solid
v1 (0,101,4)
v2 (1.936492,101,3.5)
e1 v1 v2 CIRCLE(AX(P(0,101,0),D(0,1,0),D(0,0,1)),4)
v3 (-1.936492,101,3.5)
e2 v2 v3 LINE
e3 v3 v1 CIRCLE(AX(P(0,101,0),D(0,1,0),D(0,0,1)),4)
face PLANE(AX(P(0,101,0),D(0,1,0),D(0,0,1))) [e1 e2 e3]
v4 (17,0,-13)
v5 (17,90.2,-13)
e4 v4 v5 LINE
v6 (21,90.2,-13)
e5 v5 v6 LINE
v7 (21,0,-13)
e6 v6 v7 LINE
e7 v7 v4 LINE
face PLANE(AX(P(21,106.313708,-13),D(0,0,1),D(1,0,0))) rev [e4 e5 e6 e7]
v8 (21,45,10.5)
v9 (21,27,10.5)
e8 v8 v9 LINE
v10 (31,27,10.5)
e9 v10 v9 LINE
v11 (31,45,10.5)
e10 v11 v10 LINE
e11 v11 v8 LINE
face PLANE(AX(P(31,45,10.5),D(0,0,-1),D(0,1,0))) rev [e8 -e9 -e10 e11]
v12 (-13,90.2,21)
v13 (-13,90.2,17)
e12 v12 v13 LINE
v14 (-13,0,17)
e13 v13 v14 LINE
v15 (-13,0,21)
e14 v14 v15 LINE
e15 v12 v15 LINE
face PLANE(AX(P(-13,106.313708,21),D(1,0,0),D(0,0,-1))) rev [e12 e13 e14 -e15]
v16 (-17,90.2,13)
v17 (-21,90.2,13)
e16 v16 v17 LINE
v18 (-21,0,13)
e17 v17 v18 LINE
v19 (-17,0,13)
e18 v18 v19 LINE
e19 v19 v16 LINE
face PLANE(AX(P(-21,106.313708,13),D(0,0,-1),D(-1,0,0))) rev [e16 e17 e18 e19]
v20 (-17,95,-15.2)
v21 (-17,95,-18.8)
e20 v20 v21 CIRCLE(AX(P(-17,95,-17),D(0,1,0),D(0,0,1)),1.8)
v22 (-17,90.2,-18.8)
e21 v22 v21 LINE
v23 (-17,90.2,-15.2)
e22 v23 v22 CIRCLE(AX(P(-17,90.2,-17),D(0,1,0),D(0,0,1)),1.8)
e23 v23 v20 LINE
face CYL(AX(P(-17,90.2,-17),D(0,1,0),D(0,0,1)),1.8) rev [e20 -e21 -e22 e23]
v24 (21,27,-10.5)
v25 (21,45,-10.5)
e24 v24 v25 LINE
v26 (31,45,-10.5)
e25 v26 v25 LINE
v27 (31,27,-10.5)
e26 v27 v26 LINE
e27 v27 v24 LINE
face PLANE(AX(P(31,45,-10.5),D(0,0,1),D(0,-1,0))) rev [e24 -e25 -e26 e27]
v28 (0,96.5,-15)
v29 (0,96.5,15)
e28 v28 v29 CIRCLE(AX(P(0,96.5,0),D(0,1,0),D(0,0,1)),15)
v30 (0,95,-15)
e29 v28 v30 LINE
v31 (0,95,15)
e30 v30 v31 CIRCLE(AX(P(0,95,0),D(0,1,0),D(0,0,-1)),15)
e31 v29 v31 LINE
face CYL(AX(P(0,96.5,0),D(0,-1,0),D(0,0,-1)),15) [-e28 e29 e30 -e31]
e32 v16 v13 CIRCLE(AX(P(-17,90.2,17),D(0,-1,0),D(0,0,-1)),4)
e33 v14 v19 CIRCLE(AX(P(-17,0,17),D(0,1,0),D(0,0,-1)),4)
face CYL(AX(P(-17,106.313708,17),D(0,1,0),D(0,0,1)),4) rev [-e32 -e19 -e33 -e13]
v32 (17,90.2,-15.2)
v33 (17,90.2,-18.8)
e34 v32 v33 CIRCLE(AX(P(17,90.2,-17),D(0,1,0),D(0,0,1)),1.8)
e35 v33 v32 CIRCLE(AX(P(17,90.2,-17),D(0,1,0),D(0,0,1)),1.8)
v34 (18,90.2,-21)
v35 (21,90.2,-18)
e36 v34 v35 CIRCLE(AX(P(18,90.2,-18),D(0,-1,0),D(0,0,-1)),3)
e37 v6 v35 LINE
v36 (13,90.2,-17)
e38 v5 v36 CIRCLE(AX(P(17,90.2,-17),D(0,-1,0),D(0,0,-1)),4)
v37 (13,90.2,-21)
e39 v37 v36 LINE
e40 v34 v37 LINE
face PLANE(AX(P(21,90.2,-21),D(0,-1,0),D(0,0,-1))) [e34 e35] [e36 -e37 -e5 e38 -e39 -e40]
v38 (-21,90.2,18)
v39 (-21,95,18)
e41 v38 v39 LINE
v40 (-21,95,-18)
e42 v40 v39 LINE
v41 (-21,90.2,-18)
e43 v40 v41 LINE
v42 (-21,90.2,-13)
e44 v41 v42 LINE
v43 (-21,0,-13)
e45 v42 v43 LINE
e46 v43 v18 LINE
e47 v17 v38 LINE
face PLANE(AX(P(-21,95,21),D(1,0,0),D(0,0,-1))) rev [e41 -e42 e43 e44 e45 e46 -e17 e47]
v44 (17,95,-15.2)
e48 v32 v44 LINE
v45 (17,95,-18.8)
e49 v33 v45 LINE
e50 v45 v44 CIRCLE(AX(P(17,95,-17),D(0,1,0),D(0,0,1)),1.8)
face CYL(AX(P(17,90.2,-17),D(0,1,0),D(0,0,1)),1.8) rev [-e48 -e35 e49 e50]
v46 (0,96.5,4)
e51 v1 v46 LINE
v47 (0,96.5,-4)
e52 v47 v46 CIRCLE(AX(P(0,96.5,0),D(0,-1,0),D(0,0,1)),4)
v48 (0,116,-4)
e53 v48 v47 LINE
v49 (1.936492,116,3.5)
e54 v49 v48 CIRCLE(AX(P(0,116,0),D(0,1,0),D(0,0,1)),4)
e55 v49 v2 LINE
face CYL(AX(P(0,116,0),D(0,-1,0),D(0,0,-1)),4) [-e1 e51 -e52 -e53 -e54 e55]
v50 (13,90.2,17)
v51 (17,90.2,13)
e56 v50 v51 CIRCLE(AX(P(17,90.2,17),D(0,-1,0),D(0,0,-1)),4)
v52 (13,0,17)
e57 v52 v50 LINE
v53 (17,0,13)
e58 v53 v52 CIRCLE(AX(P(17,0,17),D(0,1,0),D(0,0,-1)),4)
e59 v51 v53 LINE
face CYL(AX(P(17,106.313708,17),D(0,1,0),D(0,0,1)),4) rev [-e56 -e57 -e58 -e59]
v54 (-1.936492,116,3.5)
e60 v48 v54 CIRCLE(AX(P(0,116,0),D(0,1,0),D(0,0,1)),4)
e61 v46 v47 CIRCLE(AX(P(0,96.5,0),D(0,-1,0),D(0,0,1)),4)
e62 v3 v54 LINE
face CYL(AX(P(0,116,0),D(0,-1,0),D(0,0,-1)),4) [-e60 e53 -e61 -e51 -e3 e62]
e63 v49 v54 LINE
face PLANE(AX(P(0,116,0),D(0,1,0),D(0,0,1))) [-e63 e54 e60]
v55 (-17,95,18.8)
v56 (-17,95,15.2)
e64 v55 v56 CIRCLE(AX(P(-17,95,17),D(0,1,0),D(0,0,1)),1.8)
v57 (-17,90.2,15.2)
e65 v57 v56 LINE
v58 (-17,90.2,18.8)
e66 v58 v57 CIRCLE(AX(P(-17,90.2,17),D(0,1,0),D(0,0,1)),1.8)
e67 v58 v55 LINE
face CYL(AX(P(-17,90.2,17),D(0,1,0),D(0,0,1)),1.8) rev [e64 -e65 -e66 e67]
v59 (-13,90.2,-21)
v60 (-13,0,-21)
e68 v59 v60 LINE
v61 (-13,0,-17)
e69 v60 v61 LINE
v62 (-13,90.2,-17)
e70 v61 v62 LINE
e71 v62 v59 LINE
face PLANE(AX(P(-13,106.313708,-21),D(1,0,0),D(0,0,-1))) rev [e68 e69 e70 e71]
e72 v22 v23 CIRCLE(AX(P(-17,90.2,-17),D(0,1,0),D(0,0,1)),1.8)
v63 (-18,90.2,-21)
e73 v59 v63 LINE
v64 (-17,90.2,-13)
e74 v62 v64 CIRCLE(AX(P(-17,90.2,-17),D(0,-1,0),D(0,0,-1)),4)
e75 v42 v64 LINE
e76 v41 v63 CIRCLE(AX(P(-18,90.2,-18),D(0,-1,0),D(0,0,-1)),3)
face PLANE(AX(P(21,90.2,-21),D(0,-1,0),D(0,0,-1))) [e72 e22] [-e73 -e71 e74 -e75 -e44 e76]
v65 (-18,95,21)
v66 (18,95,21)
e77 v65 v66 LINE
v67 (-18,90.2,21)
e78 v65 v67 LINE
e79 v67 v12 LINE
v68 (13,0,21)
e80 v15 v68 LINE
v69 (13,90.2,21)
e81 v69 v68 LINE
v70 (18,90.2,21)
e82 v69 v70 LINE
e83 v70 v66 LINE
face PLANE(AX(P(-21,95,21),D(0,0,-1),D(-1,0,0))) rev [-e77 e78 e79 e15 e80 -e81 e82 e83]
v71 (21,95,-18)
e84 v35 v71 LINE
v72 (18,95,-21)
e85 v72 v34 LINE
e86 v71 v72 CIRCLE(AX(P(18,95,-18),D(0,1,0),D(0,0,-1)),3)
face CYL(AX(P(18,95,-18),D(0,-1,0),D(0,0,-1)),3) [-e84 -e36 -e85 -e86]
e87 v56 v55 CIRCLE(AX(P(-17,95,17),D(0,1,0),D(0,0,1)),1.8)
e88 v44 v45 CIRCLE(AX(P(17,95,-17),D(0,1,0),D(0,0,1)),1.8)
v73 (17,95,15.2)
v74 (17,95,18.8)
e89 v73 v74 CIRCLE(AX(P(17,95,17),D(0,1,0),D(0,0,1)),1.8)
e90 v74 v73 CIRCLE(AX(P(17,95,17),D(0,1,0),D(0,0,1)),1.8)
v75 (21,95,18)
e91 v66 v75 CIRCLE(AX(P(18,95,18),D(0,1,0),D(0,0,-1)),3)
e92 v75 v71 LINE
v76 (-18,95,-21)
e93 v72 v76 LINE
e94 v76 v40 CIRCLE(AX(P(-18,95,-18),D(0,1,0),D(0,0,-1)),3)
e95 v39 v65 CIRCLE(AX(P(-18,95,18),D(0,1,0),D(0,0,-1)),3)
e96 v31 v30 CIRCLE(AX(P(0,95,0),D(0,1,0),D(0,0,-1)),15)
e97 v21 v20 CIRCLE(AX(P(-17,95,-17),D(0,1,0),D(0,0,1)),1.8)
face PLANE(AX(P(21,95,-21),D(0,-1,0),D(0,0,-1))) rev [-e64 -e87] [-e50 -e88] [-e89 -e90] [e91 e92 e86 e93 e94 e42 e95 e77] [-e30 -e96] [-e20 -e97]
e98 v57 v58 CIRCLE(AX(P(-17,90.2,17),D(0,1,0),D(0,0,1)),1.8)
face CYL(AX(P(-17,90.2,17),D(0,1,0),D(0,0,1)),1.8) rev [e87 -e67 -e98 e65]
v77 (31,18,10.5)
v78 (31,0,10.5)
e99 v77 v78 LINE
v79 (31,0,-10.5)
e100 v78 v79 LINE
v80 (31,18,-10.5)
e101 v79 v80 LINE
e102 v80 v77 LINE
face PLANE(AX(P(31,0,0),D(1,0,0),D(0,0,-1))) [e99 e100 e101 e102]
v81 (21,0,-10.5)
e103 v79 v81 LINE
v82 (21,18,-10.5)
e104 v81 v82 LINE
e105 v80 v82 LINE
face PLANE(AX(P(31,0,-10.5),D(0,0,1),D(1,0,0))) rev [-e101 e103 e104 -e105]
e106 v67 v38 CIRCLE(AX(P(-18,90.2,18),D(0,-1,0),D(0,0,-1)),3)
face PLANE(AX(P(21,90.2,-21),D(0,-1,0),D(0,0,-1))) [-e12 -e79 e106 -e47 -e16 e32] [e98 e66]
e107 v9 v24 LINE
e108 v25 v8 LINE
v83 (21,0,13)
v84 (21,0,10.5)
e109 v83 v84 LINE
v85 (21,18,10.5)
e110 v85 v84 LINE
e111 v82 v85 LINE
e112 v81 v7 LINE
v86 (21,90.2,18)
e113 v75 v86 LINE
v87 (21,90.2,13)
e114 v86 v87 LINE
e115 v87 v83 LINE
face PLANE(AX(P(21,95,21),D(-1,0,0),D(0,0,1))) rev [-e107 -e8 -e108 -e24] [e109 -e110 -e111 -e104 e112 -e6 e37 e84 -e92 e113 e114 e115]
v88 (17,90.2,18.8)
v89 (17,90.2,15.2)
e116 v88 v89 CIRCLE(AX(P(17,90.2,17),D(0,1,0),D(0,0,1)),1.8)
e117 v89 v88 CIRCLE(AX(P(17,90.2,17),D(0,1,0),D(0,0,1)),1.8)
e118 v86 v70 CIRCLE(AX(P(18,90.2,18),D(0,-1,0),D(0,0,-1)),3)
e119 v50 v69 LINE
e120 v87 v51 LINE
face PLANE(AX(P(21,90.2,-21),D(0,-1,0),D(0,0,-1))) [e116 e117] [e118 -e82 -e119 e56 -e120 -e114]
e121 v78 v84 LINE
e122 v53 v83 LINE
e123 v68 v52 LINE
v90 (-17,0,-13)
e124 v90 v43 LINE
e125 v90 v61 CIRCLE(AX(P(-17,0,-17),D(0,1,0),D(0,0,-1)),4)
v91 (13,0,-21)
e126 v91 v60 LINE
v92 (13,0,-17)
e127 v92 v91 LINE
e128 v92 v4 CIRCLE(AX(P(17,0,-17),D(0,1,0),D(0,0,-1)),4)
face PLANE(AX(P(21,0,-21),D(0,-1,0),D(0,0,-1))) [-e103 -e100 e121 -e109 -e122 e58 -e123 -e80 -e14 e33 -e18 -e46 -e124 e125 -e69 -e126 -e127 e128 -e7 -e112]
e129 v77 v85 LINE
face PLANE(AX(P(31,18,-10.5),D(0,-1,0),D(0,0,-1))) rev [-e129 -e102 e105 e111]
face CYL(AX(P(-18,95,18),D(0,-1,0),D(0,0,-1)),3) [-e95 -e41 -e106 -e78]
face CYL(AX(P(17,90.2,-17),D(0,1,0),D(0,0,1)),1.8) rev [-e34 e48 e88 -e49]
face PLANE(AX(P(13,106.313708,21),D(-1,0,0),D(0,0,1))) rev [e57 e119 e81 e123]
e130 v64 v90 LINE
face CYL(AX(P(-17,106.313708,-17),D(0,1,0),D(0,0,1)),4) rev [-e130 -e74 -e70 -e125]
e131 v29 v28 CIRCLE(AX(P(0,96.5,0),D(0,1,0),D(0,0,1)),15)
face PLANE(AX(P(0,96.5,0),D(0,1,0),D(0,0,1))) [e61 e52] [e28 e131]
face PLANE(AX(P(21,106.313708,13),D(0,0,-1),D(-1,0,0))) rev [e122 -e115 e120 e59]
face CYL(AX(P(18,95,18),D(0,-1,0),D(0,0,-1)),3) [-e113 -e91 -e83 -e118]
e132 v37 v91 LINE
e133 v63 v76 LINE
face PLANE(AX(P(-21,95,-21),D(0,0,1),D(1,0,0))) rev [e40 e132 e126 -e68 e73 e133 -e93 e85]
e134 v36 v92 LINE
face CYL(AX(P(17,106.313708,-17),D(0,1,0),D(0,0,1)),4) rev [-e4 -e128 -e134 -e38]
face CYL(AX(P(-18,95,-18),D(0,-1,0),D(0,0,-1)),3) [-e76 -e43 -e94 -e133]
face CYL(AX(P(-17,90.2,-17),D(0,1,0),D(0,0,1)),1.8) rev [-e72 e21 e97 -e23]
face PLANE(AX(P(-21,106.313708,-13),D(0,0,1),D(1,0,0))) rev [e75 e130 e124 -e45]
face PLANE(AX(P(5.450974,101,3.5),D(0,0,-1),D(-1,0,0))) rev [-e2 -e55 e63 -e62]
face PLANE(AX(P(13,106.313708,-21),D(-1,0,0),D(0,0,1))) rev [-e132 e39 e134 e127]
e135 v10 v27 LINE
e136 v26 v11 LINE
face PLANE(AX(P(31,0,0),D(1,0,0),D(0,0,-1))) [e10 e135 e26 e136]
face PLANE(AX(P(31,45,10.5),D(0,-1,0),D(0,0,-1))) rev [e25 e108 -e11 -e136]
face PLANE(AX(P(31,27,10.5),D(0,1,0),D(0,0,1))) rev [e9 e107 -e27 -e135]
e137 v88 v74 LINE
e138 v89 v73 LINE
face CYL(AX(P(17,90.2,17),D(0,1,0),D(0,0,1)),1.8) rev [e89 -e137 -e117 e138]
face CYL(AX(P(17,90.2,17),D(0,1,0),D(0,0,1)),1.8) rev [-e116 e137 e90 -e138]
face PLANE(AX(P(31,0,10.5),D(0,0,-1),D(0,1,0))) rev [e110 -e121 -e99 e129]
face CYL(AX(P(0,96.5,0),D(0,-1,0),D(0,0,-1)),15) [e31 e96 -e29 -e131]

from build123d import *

# Parameters (mm, degrees)
SKETCH1_W           = 42
SKETCH1_H           = 42
BOSS_EXTRUDE1_DEPTH = 95
SKETCH2_W           = 8
SKETCH2_H           = 8
CUT_EXTRUDE1_DEPTH  = 90.2
SKETCH3_R           = 1.8
CUT_EXTRUDE2_DEPTH  = 4.8
FILLET1_R           = 4
SKETCH4_R           = 15
BOSS_EXTRUDE2_DEPTH = 1.5
SKETCH5_R           = 4
BOSS_EXTRUDE3_DEPTH = 21
FILLET2_R           = 3
SKETCH8_W           = 21
SKETCH8_H           = 18
BOSS_EXTRUDE5_DEPTH = 10
SKETCH9_W           = 13.716177762
SKETCH9_H           = 4.011335006
CUT_EXTRUDE3_DEPTH  = 15


with BuildPart() as part:
    # Sketch1 → Boss-Extrude1 (new body)
    with BuildSketch(Plane(origin=(0, 0, 0), x_dir=(1, 0, 0), z_dir=(0, 1, 0))):
        Rectangle(SKETCH1_W, SKETCH1_H)
    extrude(amount=BOSS_EXTRUDE1_DEPTH)

    # Sketch2 → Cut-Extrude1 (cut)
    with BuildSketch(Plane.XZ):
        with Locations((-17, 17)):
            Rectangle(SKETCH2_W, SKETCH2_H)
        with Locations((17, 17)):
            Rectangle(SKETCH2_W, SKETCH2_H)
        with Locations((-17, -17)):
            Rectangle(SKETCH2_W, SKETCH2_H)
        with Locations((17, -17)):
            Rectangle(SKETCH2_W, SKETCH2_H)
    extrude(amount=-CUT_EXTRUDE1_DEPTH, mode=Mode.SUBTRACT)

    # Sketch3 → Cut-Extrude2 (cut)
    with BuildSketch(Plane(origin=(0, 95, 0), x_dir=(1, 0, 0), z_dir=(0, 1, 0))):
        with Locations(Location((-17, 17, 0), (0, 0, 270))):
            Circle(SKETCH3_R)
        with Locations(Location((17, 17, 0), (0, 0, 270))):
            Circle(SKETCH3_R)
        with Locations(Location((-17, -17, 0), (0, 0, 270))):
            Circle(SKETCH3_R)
        with Locations(Location((17, -17, 0), (0, 0, 270))):
            Circle(SKETCH3_R)
    extrude(amount=-CUT_EXTRUDE2_DEPTH, mode=Mode.SUBTRACT)

    # Fillet1
    fillet1_edges = [part.edges().sort_by_distance(p)[0] for p in [
        (-13, 45.1, 13),
        (13, 45.1, 13),
        (-13, 45.1, -13),
        (13, 45.1, -13),
    ]]
    fillet(fillet1_edges, radius=FILLET1_R)

    # Sketch4 → Boss-Extrude2 (add)
    with BuildSketch(Plane(origin=(0, 95, 0), x_dir=(1, 0, 0), z_dir=(0, 1, 0))):
        with Locations(Location((0, 0, 0), (0, 0, 90))):
            Circle(SKETCH4_R)
    extrude(amount=BOSS_EXTRUDE2_DEPTH)

    # Sketch5 → Boss-Extrude3 (add)
    with BuildSketch(Plane(origin=(0, 95, 0), x_dir=(1, 0, 0), z_dir=(0, 1, 0))):
        with Locations(Location((0, 0, 0), (0, 0, 90))):
            Circle(SKETCH5_R)
    extrude(amount=BOSS_EXTRUDE3_DEPTH)

    # Fillet2
    fillet2_edges = [part.edges().sort_by_distance(p)[0] for p in [
        (21, 92.6, 21),
        (-21, 92.6, 21),
        (-21, 92.6, -21),
        (21, 92.6, -21),
    ]]
    fillet(fillet2_edges, radius=FILLET2_R)

    # Sketch8 → Boss-Extrude5 (add)
    with BuildSketch(Plane(origin=(21, 0, 0), x_dir=(0, 0, -1), z_dir=(1, 0, 0))):
        with Locations((0, 9)):
            Rectangle(SKETCH8_W, SKETCH8_H)
        with Locations((0, 36)):
            Rectangle(SKETCH8_W, SKETCH8_H)
    extrude(amount=BOSS_EXTRUDE5_DEPTH)

    # Sketch9 → Cut-Extrude3 (cut)
    with BuildSketch(Plane(origin=(0, 116, 0), x_dir=(1, 0, 0), z_dir=(0, 1, 0))):
        with Locations((-1.407114482, -5.505667503)):
            Rectangle(SKETCH9_W, SKETCH9_H)
    extrude(amount=-CUT_EXTRUDE3_DEPTH, mode=Mode.SUBTRACT)


solid = part.part
